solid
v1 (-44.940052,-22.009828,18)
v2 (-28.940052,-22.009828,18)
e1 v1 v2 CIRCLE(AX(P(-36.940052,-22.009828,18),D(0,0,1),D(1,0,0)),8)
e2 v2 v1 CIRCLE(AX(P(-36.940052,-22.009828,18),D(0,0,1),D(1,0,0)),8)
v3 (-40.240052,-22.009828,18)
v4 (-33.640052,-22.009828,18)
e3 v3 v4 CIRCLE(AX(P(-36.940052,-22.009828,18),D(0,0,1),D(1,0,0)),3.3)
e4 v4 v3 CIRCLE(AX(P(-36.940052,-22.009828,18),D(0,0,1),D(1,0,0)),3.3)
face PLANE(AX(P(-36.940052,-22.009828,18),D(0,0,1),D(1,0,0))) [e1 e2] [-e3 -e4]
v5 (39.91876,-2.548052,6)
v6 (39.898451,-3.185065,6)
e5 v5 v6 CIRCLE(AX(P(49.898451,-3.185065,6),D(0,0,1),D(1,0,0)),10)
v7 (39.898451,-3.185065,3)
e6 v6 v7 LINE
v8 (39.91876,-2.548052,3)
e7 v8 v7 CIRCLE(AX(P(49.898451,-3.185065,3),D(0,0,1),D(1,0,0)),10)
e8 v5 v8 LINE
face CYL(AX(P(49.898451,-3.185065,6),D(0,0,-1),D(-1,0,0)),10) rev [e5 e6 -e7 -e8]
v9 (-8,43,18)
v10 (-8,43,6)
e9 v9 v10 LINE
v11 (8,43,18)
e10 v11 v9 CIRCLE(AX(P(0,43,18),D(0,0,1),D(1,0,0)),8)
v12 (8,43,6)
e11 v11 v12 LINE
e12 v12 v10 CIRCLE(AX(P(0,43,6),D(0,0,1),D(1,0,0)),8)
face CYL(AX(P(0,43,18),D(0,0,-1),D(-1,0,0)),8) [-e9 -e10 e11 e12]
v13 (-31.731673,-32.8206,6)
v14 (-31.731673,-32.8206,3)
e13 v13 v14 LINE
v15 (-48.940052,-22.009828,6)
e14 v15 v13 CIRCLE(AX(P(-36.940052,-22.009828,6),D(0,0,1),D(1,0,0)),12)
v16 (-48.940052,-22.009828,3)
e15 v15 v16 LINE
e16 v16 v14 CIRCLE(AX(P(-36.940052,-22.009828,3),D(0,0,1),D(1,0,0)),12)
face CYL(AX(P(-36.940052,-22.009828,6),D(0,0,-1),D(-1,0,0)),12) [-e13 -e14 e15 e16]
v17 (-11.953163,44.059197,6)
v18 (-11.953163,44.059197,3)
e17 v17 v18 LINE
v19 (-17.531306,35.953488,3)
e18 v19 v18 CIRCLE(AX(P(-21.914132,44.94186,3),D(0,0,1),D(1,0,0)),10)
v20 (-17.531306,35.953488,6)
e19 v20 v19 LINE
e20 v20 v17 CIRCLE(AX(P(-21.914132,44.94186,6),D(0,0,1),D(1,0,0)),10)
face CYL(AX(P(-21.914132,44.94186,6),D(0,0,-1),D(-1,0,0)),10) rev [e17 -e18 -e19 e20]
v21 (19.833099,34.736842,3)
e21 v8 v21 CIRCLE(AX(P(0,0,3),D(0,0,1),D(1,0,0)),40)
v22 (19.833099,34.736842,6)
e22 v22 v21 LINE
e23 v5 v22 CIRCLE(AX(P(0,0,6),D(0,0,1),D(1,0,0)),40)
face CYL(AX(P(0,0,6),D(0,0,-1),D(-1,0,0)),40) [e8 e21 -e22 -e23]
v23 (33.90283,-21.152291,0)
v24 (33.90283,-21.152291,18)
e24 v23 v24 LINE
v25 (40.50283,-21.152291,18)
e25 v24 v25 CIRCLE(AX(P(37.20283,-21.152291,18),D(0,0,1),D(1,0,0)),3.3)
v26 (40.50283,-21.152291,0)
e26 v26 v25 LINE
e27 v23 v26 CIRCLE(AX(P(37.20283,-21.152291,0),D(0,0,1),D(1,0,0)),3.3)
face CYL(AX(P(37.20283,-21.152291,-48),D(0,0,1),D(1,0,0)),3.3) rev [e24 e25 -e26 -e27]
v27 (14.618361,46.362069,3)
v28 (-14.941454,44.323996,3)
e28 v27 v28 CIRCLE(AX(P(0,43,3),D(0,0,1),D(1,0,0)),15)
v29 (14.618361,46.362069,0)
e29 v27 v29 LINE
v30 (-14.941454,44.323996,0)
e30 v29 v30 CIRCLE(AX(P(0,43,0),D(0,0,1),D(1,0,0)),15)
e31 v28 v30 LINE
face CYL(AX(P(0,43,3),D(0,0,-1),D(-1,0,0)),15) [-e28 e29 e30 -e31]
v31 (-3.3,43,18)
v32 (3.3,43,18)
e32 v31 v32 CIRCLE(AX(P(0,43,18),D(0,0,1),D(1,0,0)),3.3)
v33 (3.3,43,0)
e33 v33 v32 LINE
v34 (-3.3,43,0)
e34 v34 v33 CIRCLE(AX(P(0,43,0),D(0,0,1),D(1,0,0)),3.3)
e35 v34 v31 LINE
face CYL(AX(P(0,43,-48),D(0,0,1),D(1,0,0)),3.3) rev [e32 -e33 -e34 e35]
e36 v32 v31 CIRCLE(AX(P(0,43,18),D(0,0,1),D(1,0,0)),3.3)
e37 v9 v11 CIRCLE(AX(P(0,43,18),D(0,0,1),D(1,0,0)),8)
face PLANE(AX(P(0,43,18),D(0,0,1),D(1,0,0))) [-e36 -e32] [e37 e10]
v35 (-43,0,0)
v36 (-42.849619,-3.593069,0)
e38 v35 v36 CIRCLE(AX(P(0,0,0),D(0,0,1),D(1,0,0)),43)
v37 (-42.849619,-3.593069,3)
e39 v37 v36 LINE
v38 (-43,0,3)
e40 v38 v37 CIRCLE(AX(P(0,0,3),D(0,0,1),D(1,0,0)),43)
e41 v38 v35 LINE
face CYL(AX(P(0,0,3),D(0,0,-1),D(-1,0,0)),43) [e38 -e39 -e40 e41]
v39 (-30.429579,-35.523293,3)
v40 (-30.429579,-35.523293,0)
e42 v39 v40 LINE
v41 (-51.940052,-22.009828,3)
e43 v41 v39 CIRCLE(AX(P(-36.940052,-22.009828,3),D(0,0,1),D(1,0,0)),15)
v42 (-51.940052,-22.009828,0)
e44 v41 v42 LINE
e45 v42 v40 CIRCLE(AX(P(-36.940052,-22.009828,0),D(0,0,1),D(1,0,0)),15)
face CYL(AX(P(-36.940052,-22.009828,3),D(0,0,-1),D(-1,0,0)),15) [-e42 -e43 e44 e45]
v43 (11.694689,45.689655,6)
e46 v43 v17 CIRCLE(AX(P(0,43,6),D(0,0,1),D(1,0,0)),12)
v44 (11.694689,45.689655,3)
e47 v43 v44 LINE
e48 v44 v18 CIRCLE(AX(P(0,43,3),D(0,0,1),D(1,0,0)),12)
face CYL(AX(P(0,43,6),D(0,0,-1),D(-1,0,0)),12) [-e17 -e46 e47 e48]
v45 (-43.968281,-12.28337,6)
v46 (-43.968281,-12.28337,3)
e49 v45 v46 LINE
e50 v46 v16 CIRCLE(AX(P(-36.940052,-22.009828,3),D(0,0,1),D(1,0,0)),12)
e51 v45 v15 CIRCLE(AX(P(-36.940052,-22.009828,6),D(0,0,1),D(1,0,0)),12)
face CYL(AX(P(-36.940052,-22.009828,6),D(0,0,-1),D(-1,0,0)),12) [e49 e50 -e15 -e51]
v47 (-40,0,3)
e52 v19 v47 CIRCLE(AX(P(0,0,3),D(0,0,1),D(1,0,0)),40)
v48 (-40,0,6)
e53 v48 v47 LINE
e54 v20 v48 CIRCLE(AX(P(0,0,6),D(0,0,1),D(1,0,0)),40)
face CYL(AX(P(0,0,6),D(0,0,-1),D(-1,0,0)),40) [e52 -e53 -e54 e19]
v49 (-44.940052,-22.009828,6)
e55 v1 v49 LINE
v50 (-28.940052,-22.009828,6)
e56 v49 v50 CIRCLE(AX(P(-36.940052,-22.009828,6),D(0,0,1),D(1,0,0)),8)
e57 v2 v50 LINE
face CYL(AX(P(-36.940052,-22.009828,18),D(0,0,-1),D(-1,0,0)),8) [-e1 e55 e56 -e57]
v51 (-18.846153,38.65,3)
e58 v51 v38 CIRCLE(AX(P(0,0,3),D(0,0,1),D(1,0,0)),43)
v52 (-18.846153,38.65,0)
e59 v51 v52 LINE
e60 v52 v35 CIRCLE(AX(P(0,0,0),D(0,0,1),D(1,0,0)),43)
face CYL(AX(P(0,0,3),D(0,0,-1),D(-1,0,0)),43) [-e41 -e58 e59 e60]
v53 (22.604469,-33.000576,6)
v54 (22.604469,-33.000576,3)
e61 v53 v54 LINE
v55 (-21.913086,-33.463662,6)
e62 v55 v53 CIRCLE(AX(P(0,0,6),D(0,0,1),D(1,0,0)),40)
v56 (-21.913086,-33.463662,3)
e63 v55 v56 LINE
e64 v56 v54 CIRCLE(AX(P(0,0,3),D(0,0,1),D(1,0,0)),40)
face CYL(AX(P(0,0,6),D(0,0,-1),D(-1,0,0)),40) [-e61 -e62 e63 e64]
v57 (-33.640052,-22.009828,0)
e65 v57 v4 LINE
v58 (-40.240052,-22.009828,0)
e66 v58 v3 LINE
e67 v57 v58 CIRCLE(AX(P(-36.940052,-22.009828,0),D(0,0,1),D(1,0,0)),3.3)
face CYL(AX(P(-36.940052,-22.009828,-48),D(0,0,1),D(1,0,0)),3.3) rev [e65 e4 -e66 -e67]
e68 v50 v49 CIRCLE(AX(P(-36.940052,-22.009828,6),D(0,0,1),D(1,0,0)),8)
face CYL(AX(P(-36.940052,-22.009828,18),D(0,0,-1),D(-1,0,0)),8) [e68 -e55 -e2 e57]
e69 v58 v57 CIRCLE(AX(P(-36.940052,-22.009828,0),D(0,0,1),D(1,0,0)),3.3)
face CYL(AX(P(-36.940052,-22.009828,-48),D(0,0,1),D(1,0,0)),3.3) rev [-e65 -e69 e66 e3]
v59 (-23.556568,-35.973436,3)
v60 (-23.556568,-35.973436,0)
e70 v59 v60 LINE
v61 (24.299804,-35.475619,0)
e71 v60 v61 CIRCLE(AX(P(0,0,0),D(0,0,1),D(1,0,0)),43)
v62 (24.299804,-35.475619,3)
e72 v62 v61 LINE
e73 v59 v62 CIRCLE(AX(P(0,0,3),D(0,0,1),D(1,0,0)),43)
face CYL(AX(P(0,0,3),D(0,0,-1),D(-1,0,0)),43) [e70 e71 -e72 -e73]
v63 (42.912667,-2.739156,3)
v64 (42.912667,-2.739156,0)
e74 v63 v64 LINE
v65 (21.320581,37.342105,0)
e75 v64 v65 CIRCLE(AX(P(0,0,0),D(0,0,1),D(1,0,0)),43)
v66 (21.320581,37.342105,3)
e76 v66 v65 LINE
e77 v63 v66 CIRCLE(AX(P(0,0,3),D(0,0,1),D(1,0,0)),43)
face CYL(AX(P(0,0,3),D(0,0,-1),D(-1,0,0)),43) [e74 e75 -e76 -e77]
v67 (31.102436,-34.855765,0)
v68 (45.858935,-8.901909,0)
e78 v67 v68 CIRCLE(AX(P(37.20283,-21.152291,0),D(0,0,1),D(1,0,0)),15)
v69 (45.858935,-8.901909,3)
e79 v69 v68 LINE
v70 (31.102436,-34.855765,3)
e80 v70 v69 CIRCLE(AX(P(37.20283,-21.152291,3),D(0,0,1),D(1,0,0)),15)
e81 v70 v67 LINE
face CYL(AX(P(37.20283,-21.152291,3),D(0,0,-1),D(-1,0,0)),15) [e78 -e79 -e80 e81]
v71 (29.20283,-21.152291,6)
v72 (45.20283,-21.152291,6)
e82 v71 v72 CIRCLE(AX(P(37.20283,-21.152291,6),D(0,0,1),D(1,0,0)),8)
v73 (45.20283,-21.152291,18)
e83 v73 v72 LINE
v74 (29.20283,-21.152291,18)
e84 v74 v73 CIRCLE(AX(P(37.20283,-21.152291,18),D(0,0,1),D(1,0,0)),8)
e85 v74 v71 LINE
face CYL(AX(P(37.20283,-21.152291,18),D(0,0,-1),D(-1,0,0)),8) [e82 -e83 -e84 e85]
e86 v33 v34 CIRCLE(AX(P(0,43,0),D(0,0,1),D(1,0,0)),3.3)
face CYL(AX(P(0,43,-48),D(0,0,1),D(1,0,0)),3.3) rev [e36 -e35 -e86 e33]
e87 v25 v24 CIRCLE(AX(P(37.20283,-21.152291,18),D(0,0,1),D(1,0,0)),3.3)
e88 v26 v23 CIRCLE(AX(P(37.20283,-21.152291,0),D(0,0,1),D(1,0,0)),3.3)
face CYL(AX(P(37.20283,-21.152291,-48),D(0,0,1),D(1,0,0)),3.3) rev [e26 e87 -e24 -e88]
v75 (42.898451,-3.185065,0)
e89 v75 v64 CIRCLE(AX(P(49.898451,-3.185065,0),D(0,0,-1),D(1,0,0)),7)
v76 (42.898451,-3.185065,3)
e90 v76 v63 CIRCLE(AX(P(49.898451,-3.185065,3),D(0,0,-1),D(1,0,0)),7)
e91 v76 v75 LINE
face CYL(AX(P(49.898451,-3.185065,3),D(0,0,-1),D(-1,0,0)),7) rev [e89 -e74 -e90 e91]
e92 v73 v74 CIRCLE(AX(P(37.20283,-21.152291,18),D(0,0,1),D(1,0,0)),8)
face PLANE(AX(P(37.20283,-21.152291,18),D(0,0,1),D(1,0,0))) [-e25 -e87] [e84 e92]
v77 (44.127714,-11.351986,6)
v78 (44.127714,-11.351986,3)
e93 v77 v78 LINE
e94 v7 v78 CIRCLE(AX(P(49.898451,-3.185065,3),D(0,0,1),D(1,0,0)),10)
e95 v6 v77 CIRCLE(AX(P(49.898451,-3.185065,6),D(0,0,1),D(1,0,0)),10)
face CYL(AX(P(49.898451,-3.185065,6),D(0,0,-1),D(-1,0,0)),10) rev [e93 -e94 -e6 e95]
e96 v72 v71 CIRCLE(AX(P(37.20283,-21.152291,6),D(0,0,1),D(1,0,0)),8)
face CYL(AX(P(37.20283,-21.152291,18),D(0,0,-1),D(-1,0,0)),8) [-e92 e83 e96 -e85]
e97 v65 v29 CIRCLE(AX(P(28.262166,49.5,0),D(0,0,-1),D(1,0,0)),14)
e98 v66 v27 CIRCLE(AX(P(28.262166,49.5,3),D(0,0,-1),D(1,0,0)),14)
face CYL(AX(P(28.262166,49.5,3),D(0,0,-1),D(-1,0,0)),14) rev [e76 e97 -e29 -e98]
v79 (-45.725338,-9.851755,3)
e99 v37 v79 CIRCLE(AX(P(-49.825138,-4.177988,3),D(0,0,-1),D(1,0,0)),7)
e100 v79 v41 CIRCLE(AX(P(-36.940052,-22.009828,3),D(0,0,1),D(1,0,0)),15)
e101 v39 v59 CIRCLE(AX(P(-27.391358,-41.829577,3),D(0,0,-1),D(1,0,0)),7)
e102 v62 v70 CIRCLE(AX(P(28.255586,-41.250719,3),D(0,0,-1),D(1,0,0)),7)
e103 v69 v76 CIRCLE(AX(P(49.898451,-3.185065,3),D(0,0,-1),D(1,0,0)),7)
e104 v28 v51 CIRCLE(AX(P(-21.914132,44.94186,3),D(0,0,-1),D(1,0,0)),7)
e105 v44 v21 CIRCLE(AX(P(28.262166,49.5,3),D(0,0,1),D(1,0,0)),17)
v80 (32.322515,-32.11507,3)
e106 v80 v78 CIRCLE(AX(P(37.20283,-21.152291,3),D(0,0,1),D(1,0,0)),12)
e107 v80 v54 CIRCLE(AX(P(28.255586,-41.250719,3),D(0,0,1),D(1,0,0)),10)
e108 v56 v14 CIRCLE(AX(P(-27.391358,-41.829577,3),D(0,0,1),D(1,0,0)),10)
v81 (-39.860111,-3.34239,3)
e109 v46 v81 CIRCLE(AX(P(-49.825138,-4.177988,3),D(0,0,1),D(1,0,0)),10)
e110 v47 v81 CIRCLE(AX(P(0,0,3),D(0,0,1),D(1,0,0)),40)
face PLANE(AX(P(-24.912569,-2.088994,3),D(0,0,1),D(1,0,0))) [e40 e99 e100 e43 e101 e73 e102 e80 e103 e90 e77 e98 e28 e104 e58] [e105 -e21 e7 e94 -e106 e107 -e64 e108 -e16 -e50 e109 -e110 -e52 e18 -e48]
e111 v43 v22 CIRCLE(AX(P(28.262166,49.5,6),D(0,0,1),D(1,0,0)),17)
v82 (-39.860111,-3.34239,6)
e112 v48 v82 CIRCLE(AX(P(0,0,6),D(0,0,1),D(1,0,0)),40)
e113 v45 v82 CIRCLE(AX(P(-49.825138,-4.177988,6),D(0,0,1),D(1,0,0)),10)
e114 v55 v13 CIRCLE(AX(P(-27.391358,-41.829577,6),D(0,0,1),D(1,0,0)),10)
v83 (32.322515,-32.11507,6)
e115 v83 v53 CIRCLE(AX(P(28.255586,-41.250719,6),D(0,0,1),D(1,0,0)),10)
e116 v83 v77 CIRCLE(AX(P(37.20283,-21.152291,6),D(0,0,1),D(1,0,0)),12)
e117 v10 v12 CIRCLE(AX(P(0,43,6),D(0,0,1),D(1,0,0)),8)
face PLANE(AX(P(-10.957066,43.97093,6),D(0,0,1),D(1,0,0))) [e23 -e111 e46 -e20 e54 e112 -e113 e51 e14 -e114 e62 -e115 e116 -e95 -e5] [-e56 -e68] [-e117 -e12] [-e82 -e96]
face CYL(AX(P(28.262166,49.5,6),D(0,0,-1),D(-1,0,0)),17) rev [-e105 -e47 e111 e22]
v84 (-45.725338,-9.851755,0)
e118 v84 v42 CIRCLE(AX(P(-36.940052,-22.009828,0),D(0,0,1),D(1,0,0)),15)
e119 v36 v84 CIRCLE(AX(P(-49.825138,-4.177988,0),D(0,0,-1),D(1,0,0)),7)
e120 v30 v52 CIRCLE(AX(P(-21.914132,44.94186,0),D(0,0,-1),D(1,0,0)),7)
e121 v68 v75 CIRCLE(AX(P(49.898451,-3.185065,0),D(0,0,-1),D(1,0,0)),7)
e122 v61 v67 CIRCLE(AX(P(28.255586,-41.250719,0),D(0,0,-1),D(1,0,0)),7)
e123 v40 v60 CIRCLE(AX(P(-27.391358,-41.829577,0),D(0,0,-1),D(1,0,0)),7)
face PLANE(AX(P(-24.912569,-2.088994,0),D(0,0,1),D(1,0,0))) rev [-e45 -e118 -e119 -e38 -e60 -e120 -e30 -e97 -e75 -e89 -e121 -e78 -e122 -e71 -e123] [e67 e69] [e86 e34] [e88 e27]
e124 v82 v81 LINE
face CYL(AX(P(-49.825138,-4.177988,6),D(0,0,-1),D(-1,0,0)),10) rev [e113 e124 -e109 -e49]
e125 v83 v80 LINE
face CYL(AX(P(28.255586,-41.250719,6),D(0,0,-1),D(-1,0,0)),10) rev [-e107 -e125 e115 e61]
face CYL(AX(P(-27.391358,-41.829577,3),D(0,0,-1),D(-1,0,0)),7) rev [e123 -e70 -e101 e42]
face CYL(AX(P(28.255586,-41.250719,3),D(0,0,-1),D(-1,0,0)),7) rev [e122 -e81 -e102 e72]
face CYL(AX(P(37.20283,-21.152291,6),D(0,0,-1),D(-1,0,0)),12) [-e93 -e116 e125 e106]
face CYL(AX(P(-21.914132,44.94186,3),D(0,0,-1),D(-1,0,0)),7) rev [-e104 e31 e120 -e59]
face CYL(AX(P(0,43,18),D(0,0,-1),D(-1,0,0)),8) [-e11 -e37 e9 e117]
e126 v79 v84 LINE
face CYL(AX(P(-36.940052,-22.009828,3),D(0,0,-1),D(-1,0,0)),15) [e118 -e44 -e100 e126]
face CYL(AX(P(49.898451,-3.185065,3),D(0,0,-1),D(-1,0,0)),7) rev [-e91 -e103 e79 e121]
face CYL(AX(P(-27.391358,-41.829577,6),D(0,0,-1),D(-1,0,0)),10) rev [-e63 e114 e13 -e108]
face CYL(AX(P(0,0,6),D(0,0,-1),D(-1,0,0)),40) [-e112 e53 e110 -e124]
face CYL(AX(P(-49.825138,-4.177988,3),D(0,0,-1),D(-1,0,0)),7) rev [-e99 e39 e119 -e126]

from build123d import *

# Parameters (mm, degrees)
BASE_PLATE_DEPTH               = 3
OFFSET_STEP_DEPTH              = 3
STANDOFF_BOSS_PROFILE_3X_16_R  = 8
STANDOFF_BOSSES_3X_16_DEPTH    = 12
MOUNTING_HOLE_PROFILE_3X_6_6_R = 3.3
MOUNTING_HOLES_3X_6_6_DEPTH    = 66


with BuildPart() as part:
    # Base Plate Profile → Base Plate (new body)
    with BuildSketch(Plane.XY):
        with BuildLine():
            ThreePointArc((42.912667435, -2.73915564), (37.856365651, 20.393518081), (21.320581008, 37.342105263))
            ThreePointArc((21.320581008, 37.342105263), (17.024750702, 41.150119272), (14.618361477, 46.362068966))
            ThreePointArc((14.618361477, 46.362068966), (-1.031761946, 57.964473505), (-14.941453584, 44.323995772))
            ThreePointArc((-14.941453584, 44.323995772), (-16.147655157, 40.973517523), (-18.846153454, 38.65))
            ThreePointArc((-18.846153454, 38.65), (-37.385977476, 21.243556391), (-42.849619055, -3.593069277))
            ThreePointArc((-42.849619055, -3.593069277), (-43.464441702, -7.100578343), (-45.725338247, -9.851755099))
            ThreePointArc((-45.725338247, -9.851755099), (-49.826116824, -29.687675595), (-30.429578698, -35.523293437))
            ThreePointArc((-30.429578698, -35.523293437), (-26.93387798, -34.844542215), (-23.556567678, -35.9734363))
            ThreePointArc((-23.556567678, -35.9734363), (0.447275802, -42.997673709), (24.299804013, -35.47561874))
            ThreePointArc((24.299804013, -35.47561874), (27.620379782, -34.279599541), (31.102436465, -34.855764987))
            ThreePointArc((31.102436465, -34.855764987), (50.242522242, -28.566226035), (45.85893495, -8.901909464))
            ThreePointArc((45.85893495, -8.901909464), (43.583057713, -6.204305311), (42.912667435, -2.73915564))
        make_face()
    extrude(amount=BASE_PLATE_DEPTH)

    # Offset Step Profile → Offset Step (add)
    with BuildSketch(Plane.XY.offset(3)):
        with BuildLine():
            ThreePointArc((-17.531305538, 35.953488372), (-34.777653466, 19.761447806), (-39.860110749, -3.342390025))
            ThreePointArc((-39.860110749, -3.342390025), (-40.738428815, -8.353117262), (-43.968281023, -12.283369771))
            ThreePointArc((-43.968281023, -12.283369771), (-47.248903885, -28.152106168), (-31.731673384, -32.820600441))
            ThreePointArc((-31.731673384, -32.820600441), (-26.737815215, -31.850955839), (-21.913086212, -33.463661675))
            ThreePointArc((-21.913086212, -33.463661675), (0.416070514, -39.997836008), (22.604468849, -33.000575572))
            ThreePointArc((22.604468849, -33.000575572), (27.34814852, -31.291976717), (32.32251521, -32.11507021))
            ThreePointArc((32.32251521, -32.11507021), (47.634583832, -27.083439049), (44.127713998, -11.351985792))
            ThreePointArc((44.127713998, -11.351985792), (40.876460802, -7.498265573), (39.918760405, -2.548051758))
            ThreePointArc((39.918760405, -2.548051758), (35.215223861, 18.970714494), (19.833098612, 34.736842105))
            ThreePointArc((19.833098612, 34.736842105), (14.616733241, 39.360859116), (11.694689182, 45.689655172))
            ThreePointArc((11.694689182, 45.689655172), (-0.825409557, 54.971578804), (-11.953162867, 44.059196617))
            ThreePointArc((-11.953162867, 44.059196617), (-13.676307972, 39.272799119), (-17.531305538, 35.953488372))
        make_face()
    extrude(amount=OFFSET_STEP_DEPTH)

    # Standoff Boss Profile 3xØ16 → Standoff Bosses 3xØ16 (add)
    with BuildSketch(Plane.XY.offset(6)):
        with Locations((0, 43)):
            Circle(STANDOFF_BOSS_PROFILE_3X_16_R)
        with Locations((37.202830189, -21.152291105)):
            Circle(STANDOFF_BOSS_PROFILE_3X_16_R)
        with Locations((-36.940052128, -22.009828458)):
            Circle(STANDOFF_BOSS_PROFILE_3X_16_R)
    extrude(amount=STANDOFF_BOSSES_3X_16_DEPTH)

    # Mounting Hole Profile 3xØ6.6 → Mounting Holes 3xØ6.6 (cut)
    with BuildSketch(Plane.XY.offset(18)):
        with Locations((0, 43)):
            Circle(MOUNTING_HOLE_PROFILE_3X_6_6_R)
        with Locations((37.202830189, -21.152291105)):
            Circle(MOUNTING_HOLE_PROFILE_3X_6_6_R)
        with Locations((-36.940052128, -22.009828458)):
            Circle(MOUNTING_HOLE_PROFILE_3X_6_6_R)
    extrude(amount=-MOUNTING_HOLES_3X_6_6_DEPTH, mode=Mode.SUBTRACT)


solid = part.part
